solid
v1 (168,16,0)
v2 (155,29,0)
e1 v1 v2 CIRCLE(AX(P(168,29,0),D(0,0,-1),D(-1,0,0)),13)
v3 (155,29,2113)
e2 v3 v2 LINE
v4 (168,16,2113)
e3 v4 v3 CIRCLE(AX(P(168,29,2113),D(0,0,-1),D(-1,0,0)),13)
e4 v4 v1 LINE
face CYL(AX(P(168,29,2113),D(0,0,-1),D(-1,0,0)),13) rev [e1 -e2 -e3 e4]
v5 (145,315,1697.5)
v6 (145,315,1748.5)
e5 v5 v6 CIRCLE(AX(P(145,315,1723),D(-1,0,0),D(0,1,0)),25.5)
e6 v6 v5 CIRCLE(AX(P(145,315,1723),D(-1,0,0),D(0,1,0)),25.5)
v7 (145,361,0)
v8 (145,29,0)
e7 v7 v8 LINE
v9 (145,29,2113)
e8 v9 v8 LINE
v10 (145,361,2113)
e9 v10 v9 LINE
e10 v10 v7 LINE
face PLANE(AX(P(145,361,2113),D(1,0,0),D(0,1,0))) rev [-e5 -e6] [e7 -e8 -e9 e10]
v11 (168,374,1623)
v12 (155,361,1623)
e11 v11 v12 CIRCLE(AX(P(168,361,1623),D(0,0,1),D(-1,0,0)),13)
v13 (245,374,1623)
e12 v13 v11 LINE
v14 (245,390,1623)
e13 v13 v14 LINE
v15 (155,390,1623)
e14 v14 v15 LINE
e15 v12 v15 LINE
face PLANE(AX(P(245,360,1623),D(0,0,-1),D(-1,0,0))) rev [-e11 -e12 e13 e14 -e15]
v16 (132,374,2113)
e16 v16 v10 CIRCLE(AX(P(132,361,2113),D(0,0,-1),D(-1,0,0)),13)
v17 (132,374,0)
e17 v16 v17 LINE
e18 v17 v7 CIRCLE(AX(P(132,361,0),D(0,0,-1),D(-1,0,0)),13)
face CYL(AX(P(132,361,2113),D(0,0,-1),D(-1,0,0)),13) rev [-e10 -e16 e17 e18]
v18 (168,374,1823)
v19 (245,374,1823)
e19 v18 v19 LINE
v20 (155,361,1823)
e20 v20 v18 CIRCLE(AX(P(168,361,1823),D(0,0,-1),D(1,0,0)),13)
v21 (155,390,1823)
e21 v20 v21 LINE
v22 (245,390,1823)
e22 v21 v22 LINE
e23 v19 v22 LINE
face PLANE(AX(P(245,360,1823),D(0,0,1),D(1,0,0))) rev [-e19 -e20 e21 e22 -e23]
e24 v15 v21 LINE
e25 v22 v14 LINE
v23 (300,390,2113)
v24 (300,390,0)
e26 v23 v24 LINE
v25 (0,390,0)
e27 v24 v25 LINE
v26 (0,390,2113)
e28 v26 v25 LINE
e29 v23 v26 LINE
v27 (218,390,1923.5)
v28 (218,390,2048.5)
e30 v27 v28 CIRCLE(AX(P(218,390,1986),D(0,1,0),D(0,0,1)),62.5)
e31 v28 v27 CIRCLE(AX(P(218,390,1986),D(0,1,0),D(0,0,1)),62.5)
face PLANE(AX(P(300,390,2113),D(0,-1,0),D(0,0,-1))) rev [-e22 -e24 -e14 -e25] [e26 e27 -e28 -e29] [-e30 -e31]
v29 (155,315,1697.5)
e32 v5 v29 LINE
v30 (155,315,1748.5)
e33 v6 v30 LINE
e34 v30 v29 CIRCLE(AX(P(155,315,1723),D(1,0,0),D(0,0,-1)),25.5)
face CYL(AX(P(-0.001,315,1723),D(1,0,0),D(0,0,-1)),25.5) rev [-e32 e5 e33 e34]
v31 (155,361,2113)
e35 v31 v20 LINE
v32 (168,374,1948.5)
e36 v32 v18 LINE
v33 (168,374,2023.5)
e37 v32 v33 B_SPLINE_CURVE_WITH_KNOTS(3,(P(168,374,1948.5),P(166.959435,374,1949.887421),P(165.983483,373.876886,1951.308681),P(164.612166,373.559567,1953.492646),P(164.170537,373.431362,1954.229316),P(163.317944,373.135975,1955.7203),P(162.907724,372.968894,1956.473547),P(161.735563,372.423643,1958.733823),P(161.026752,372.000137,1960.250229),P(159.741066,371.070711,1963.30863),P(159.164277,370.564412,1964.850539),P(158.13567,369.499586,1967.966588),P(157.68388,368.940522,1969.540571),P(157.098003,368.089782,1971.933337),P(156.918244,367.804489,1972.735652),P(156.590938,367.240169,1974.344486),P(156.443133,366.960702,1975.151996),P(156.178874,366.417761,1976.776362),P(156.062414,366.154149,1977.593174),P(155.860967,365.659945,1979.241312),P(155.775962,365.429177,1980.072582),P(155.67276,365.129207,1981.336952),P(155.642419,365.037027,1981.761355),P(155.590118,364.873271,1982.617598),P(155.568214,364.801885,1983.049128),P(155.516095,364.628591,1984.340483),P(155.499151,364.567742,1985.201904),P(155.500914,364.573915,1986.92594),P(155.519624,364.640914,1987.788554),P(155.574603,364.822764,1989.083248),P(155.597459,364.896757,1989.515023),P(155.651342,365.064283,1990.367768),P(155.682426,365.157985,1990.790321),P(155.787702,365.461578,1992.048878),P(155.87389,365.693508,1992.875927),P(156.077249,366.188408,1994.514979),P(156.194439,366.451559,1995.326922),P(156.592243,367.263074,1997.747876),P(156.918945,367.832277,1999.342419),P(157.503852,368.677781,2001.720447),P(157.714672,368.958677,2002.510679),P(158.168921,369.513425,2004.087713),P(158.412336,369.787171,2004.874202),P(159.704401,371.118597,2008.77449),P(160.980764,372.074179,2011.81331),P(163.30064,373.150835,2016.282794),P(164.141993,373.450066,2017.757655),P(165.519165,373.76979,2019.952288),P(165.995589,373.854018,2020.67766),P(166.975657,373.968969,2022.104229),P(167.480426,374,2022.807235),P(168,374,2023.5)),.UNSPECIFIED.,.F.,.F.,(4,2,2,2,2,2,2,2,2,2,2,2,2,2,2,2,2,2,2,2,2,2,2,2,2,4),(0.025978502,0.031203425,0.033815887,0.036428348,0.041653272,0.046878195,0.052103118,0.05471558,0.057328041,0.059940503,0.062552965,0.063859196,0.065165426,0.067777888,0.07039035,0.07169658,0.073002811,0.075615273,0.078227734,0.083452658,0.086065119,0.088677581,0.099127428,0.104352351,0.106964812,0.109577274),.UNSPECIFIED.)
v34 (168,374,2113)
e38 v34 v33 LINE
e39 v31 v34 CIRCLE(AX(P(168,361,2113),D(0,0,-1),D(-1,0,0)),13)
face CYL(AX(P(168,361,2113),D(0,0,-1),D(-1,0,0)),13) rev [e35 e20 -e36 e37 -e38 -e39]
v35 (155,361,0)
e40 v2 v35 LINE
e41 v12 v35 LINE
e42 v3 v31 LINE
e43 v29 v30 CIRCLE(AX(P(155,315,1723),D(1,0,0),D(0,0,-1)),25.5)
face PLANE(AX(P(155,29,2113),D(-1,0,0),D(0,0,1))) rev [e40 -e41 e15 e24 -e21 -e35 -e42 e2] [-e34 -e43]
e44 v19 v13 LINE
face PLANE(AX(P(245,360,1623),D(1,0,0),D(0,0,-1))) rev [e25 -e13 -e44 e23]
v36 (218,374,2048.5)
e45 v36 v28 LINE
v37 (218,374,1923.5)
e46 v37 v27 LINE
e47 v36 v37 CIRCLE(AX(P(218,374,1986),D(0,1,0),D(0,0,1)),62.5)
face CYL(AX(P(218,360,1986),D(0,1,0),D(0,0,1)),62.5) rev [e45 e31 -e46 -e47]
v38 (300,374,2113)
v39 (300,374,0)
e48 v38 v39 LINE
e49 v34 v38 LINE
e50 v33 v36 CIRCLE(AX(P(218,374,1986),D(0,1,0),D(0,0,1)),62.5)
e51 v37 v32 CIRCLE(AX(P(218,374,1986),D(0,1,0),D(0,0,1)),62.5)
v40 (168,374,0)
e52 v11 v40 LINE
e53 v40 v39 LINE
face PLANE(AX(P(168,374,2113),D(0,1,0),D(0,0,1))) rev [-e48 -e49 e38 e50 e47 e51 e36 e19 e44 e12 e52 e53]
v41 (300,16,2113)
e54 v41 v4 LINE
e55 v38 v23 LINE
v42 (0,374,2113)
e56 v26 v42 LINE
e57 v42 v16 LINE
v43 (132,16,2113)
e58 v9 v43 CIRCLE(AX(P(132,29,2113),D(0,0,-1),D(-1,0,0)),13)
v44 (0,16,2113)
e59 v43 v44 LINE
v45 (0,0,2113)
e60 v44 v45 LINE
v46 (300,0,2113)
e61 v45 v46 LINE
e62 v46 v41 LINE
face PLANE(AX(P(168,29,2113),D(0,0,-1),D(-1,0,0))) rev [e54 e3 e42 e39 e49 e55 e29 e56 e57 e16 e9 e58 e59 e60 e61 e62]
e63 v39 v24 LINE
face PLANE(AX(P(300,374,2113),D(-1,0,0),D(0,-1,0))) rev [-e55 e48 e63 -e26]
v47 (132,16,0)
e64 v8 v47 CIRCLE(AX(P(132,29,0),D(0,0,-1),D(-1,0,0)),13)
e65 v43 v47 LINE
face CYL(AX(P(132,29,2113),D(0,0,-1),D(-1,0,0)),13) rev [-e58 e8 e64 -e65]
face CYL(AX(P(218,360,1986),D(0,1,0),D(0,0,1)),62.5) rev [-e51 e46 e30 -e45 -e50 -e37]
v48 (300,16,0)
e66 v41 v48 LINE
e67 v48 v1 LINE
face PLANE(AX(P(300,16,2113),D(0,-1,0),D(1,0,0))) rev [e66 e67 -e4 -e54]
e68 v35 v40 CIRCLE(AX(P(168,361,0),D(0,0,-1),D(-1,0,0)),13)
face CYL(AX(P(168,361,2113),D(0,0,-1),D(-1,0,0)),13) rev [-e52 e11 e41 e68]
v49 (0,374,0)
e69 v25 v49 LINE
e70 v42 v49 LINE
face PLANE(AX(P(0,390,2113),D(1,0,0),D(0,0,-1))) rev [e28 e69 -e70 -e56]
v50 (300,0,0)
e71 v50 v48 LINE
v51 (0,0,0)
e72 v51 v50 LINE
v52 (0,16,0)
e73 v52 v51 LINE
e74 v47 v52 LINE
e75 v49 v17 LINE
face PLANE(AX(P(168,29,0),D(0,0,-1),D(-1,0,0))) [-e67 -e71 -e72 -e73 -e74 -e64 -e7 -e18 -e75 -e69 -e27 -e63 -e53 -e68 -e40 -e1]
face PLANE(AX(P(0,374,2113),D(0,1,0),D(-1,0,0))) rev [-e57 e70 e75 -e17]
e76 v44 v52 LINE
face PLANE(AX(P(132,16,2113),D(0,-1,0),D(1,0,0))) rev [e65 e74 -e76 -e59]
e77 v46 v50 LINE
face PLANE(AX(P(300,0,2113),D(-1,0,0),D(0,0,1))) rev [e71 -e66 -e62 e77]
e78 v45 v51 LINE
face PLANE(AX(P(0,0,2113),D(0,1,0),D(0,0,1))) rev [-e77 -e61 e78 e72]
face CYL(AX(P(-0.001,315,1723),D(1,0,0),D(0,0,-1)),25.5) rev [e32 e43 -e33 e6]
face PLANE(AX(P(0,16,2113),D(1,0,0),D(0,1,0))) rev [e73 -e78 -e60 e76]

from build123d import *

# Parameters (mm, degrees)
BOSS_EXTRUDE1_DEPTH = 2113
SKETCH2_R           = 62.5
SKETCH2_W           = 90
SKETCH2_H           = 200
CUT_EXTRUDE1_DEPTH  = 30
CUT_EXTRUDE2_REACH  = 2156.273
SKETCH3_R           = 25.5


with BuildPart() as part:
    # Sketch1 → Boss-Extrude1 (new body)
    with BuildSketch(Plane.XY):
        with BuildLine():
            Line((0, 0), (300, 0))
            Line((300, 0), (300, 16))
            Line((300, 16), (168, 16))
            ThreePointArc((168, 16), (158.807611845, 19.807611845), (155, 29))
            Line((155, 29), (155, 361))
            ThreePointArc((155, 361), (158.807611845, 370.192388155), (168, 374))
            Line((168, 374), (300, 374))
            Line((300, 374), (300, 390))
            Line((300, 390), (0, 390))
            Line((0, 390), (0, 374))
            Line((0, 374), (132, 374))
            ThreePointArc((132, 374), (141.192388155, 370.192388155), (145, 361))
            Line((145, 361), (145, 29))
            ThreePointArc((145, 29), (141.192388155, 19.807611845), (132, 16))
            Line((132, 16), (0, 16))
            Line((0, 16), (0, 0))
        make_face()
    extrude(amount=BOSS_EXTRUDE1_DEPTH)

    # Sketch2 → Cut-Extrude1 (cut)
    with BuildSketch(Plane(origin=(0, 390, 0), x_dir=(1, 0, 0), z_dir=(0, 1, 0))):
        with Locations(Location((218, -1986, 0), (0, 0, 270))):
            Circle(SKETCH2_R)
        with Locations((200, -1723)):
            Rectangle(SKETCH2_W, SKETCH2_H)
    extrude(amount=-CUT_EXTRUDE1_DEPTH, mode=Mode.SUBTRACT)

    # Sketch3 → Cut-Extrude2 (cut, up to next)
    with BuildSketch(Plane(origin=(155, 0, 0), x_dir=(0, 0, -1), z_dir=(1, 0, 0)), mode=Mode.PRIVATE) as cut_extrude2_sk1:
        with Locations((-1723, 315)):
            Circle(SKETCH3_R)
    cut_extrude2_tool1 = extrude(cut_extrude2_sk1.sketch, amount=-CUT_EXTRUDE2_REACH, mode=Mode.PRIVATE) & part.part
    add(cut_extrude2_tool1.solids().sort_by_distance((155, 315, 1723))[0], mode=Mode.SUBTRACT)


solid = part.part
